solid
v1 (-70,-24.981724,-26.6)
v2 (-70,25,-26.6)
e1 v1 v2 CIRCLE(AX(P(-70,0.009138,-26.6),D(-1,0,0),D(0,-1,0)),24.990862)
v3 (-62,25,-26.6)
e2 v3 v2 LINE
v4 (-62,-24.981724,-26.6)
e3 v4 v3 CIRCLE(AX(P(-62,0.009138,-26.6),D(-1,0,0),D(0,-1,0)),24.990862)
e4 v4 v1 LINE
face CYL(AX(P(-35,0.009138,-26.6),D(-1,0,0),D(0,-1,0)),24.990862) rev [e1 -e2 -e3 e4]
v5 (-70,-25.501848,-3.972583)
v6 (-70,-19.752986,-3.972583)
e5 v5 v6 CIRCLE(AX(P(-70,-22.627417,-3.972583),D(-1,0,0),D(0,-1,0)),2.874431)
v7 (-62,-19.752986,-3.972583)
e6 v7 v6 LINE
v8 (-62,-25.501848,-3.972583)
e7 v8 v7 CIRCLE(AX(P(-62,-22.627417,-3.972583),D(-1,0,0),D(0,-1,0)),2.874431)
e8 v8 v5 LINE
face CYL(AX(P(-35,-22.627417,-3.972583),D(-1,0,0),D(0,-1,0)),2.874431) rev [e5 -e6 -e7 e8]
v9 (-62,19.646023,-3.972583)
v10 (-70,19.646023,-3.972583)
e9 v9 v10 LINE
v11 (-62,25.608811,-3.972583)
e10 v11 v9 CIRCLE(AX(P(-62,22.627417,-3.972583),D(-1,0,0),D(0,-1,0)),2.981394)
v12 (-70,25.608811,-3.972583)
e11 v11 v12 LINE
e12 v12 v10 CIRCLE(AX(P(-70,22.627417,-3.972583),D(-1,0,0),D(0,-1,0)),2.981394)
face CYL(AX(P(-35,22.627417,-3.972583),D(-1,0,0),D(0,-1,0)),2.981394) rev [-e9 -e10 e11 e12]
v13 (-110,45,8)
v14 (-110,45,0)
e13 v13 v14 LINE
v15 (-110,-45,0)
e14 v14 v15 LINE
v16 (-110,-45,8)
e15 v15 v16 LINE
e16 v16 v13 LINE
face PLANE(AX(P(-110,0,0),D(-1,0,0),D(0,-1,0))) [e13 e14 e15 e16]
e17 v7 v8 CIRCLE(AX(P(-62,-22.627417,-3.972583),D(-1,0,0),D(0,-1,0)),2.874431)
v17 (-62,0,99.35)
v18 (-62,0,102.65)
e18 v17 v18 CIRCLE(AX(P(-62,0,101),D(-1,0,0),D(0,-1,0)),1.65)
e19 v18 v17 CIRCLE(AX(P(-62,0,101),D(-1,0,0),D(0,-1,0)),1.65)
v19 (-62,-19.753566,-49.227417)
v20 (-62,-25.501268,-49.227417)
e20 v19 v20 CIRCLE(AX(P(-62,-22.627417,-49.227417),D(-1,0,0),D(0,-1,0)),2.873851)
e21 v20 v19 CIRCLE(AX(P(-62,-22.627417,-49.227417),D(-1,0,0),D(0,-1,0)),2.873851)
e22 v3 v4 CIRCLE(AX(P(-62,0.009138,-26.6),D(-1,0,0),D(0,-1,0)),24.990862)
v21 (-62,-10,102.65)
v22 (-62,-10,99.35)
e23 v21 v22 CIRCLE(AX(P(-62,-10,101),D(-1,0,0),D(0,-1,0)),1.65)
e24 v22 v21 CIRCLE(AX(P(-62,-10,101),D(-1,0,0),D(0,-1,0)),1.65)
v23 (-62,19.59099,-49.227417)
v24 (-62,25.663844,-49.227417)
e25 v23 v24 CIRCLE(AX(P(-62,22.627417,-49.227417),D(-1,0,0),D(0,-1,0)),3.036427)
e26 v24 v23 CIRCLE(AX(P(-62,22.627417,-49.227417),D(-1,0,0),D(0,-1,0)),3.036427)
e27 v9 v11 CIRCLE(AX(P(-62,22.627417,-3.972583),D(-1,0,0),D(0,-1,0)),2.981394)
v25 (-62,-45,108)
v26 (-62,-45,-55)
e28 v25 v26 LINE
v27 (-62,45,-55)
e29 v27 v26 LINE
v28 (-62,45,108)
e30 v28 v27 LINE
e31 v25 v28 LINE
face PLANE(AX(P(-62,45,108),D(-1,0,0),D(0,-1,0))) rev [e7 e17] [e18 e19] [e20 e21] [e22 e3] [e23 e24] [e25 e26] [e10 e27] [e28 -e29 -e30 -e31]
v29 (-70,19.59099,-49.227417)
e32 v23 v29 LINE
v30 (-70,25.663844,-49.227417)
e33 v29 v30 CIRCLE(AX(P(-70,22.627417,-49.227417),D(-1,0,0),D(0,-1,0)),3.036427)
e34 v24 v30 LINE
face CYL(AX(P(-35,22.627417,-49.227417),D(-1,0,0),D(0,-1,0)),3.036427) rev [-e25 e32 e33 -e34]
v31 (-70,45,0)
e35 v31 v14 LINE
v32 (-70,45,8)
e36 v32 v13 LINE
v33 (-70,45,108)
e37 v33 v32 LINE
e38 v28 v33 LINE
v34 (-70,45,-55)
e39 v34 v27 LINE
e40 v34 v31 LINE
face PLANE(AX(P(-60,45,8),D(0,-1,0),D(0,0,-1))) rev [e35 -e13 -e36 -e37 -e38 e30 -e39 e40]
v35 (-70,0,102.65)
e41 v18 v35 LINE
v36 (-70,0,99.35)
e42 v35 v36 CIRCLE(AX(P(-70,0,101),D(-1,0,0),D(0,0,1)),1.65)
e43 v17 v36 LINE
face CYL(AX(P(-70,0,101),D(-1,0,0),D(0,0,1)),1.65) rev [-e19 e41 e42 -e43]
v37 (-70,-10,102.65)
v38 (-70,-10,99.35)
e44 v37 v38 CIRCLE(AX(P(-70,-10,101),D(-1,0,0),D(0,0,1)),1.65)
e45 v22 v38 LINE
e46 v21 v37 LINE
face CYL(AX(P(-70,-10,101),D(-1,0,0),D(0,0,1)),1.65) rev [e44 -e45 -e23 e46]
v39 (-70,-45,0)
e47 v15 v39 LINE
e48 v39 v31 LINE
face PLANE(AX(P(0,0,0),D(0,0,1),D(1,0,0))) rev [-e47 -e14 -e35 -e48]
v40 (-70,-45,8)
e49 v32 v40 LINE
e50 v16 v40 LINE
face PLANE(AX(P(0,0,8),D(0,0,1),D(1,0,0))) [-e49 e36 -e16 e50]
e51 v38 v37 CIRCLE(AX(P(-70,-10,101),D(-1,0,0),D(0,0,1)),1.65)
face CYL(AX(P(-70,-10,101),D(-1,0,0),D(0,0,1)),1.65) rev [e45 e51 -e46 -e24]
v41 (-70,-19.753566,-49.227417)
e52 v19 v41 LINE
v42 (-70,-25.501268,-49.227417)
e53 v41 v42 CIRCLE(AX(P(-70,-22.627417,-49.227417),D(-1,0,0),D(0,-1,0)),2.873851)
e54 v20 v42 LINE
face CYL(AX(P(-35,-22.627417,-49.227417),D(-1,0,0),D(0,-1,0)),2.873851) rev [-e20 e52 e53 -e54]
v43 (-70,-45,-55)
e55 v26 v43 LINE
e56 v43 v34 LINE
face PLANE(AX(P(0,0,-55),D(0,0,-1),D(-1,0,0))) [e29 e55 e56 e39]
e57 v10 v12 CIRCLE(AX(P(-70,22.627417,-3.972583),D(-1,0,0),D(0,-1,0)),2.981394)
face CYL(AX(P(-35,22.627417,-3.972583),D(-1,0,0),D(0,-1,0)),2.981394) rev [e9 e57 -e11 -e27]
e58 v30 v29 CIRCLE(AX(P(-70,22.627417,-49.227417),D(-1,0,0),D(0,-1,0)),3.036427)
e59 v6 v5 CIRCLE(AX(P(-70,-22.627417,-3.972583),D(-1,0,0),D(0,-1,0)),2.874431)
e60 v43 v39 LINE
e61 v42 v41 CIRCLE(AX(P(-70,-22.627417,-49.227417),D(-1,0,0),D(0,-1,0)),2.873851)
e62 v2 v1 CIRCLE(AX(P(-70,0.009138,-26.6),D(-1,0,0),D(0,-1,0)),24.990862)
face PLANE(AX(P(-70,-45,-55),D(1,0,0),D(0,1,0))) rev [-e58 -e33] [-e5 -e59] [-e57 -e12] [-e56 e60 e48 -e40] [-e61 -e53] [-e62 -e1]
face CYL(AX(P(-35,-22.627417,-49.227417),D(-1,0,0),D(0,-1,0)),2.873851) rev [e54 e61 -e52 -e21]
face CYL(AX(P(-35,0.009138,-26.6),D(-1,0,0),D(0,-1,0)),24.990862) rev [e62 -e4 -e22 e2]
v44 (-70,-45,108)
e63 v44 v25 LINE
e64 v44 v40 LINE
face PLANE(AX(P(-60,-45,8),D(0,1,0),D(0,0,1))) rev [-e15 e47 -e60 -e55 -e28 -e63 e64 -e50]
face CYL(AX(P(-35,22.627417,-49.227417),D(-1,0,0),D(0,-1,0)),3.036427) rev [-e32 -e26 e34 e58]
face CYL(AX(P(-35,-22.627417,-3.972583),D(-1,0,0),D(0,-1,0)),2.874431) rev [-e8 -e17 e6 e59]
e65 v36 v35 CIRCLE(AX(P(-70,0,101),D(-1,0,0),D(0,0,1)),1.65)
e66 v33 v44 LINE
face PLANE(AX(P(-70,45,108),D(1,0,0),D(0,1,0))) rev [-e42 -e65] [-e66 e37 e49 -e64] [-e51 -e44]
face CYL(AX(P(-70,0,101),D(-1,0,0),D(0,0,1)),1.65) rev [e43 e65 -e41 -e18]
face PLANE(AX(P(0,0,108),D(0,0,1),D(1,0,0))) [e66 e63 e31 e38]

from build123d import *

# Parameters (mm, degrees)
SKETCH1_W             = 120
SKETCH1_H             = 90
SKETCH1_R             = 40
BOSS_EXTRUDE1_DEPTH   = 8
SKETCH3_W             = 8
SKETCH3_H             = 90
BOSS_EXTRUDE2_DEPTH   = 50
SKETCH4_W             = 8
SKETCH4_H             = 90
BOSS_EXTRUDE3_DEPTH   = 100
SKETCH5_W             = 178.684775764
SKETCH5_H             = 148.432517326
CUT_EXTRUDE1_DEPTH    = 156.32224567
SKETCH6_W             = 8
SKETCH6_H             = 90
BOSS_EXTRUDE4_DEPTH   = 55
SKETCH7_R             = 3.03642696
SKETCH7_R_2           = 2.873850802
SKETCH7_R_3           = 2.874430555
SKETCH7_R_4           = 2.981394427
SKETCH7_R_5           = 24.990861791
CUT_EXTRUDE2_DEPTH    = 35
M4_TAPPED_HOLE1_D     = 3.3
M4_TAPPED_HOLE1_DEPTH = 10.1
M4_TAPPED_HOLE1_TIP   = 0.991420021


with BuildPart() as part:
    # Sketch1 → Boss-Extrude1 (new body)
    with BuildSketch(Plane.XY):
        Rectangle(SKETCH1_W, SKETCH1_H)
        Circle(SKETCH1_R, mode=Mode.SUBTRACT)
    extrude(amount=BOSS_EXTRUDE1_DEPTH)

    # Sketch3 → Boss-Extrude2 (add)
    with BuildSketch(Plane.ZY.offset(60)):
        with Locations((4, 0)):
            Rectangle(SKETCH3_W, SKETCH3_H)
    extrude(amount=BOSS_EXTRUDE2_DEPTH)

    # Sketch4 → Boss-Extrude3 (add)
    with BuildSketch(Plane.XY.offset(8)):
        with Locations((-66, 0)):
            Rectangle(SKETCH4_W, SKETCH4_H)
    extrude(amount=BOSS_EXTRUDE3_DEPTH)

    # Sketch5 → Cut-Extrude1 (cut, through all)
    with BuildSketch(Plane.XY.offset(8)):
        with Locations((27.342387882, -29.216258663)):
            Rectangle(SKETCH5_W, SKETCH5_H)
    extrude(amount=-CUT_EXTRUDE1_DEPTH, mode=Mode.SUBTRACT)

    # Sketch6 → Boss-Extrude4 (add)
    with BuildSketch(Plane(origin=(0, 0, 0), x_dir=(-1, 0, 0), z_dir=(0, 0, -1))):
        with Locations((66, 0)):
            Rectangle(SKETCH6_W, SKETCH6_H)
    extrude(amount=BOSS_EXTRUDE4_DEPTH)

    # Sketch7 → Cut-Extrude2 (cut)
    with BuildSketch(Plane.ZY.offset(70)):
        with Locations(Location((-49.227416998, 22.627416998, 0), (0, 0, 270))):
            Circle(SKETCH7_R)
        with Locations(Location((-49.227416998, -22.627416998, 0), (0, 0, 270))):
            Circle(SKETCH7_R_2)
        with Locations(Location((-3.972583002, -22.627416998, 0), (0, 0, 270))):
            Circle(SKETCH7_R_3)
        with Locations(Location((-3.972583002, 22.627416998, 0), (0, 0, 270))):
            Circle(SKETCH7_R_4)
        with Locations(Location((-26.59999988, 0.009138209, 0), (0, 0, 270))):
            Circle(SKETCH7_R_5)
    extrude(amount=-CUT_EXTRUDE2_DEPTH, mode=Mode.SUBTRACT)

    # M4 Tapped Hole1
    with Locations(Plane.ZY.offset(70)):
        with Locations((101, 0), (101, -10)):
            Hole(M4_TAPPED_HOLE1_D / 2, depth=M4_TAPPED_HOLE1_DEPTH)
            with Locations((0, 0, -(M4_TAPPED_HOLE1_DEPTH + M4_TAPPED_HOLE1_TIP / 2))):  # 118° drill point
                Cone(0, M4_TAPPED_HOLE1_D / 2, M4_TAPPED_HOLE1_TIP, mode=Mode.SUBTRACT)


solid = part.part
